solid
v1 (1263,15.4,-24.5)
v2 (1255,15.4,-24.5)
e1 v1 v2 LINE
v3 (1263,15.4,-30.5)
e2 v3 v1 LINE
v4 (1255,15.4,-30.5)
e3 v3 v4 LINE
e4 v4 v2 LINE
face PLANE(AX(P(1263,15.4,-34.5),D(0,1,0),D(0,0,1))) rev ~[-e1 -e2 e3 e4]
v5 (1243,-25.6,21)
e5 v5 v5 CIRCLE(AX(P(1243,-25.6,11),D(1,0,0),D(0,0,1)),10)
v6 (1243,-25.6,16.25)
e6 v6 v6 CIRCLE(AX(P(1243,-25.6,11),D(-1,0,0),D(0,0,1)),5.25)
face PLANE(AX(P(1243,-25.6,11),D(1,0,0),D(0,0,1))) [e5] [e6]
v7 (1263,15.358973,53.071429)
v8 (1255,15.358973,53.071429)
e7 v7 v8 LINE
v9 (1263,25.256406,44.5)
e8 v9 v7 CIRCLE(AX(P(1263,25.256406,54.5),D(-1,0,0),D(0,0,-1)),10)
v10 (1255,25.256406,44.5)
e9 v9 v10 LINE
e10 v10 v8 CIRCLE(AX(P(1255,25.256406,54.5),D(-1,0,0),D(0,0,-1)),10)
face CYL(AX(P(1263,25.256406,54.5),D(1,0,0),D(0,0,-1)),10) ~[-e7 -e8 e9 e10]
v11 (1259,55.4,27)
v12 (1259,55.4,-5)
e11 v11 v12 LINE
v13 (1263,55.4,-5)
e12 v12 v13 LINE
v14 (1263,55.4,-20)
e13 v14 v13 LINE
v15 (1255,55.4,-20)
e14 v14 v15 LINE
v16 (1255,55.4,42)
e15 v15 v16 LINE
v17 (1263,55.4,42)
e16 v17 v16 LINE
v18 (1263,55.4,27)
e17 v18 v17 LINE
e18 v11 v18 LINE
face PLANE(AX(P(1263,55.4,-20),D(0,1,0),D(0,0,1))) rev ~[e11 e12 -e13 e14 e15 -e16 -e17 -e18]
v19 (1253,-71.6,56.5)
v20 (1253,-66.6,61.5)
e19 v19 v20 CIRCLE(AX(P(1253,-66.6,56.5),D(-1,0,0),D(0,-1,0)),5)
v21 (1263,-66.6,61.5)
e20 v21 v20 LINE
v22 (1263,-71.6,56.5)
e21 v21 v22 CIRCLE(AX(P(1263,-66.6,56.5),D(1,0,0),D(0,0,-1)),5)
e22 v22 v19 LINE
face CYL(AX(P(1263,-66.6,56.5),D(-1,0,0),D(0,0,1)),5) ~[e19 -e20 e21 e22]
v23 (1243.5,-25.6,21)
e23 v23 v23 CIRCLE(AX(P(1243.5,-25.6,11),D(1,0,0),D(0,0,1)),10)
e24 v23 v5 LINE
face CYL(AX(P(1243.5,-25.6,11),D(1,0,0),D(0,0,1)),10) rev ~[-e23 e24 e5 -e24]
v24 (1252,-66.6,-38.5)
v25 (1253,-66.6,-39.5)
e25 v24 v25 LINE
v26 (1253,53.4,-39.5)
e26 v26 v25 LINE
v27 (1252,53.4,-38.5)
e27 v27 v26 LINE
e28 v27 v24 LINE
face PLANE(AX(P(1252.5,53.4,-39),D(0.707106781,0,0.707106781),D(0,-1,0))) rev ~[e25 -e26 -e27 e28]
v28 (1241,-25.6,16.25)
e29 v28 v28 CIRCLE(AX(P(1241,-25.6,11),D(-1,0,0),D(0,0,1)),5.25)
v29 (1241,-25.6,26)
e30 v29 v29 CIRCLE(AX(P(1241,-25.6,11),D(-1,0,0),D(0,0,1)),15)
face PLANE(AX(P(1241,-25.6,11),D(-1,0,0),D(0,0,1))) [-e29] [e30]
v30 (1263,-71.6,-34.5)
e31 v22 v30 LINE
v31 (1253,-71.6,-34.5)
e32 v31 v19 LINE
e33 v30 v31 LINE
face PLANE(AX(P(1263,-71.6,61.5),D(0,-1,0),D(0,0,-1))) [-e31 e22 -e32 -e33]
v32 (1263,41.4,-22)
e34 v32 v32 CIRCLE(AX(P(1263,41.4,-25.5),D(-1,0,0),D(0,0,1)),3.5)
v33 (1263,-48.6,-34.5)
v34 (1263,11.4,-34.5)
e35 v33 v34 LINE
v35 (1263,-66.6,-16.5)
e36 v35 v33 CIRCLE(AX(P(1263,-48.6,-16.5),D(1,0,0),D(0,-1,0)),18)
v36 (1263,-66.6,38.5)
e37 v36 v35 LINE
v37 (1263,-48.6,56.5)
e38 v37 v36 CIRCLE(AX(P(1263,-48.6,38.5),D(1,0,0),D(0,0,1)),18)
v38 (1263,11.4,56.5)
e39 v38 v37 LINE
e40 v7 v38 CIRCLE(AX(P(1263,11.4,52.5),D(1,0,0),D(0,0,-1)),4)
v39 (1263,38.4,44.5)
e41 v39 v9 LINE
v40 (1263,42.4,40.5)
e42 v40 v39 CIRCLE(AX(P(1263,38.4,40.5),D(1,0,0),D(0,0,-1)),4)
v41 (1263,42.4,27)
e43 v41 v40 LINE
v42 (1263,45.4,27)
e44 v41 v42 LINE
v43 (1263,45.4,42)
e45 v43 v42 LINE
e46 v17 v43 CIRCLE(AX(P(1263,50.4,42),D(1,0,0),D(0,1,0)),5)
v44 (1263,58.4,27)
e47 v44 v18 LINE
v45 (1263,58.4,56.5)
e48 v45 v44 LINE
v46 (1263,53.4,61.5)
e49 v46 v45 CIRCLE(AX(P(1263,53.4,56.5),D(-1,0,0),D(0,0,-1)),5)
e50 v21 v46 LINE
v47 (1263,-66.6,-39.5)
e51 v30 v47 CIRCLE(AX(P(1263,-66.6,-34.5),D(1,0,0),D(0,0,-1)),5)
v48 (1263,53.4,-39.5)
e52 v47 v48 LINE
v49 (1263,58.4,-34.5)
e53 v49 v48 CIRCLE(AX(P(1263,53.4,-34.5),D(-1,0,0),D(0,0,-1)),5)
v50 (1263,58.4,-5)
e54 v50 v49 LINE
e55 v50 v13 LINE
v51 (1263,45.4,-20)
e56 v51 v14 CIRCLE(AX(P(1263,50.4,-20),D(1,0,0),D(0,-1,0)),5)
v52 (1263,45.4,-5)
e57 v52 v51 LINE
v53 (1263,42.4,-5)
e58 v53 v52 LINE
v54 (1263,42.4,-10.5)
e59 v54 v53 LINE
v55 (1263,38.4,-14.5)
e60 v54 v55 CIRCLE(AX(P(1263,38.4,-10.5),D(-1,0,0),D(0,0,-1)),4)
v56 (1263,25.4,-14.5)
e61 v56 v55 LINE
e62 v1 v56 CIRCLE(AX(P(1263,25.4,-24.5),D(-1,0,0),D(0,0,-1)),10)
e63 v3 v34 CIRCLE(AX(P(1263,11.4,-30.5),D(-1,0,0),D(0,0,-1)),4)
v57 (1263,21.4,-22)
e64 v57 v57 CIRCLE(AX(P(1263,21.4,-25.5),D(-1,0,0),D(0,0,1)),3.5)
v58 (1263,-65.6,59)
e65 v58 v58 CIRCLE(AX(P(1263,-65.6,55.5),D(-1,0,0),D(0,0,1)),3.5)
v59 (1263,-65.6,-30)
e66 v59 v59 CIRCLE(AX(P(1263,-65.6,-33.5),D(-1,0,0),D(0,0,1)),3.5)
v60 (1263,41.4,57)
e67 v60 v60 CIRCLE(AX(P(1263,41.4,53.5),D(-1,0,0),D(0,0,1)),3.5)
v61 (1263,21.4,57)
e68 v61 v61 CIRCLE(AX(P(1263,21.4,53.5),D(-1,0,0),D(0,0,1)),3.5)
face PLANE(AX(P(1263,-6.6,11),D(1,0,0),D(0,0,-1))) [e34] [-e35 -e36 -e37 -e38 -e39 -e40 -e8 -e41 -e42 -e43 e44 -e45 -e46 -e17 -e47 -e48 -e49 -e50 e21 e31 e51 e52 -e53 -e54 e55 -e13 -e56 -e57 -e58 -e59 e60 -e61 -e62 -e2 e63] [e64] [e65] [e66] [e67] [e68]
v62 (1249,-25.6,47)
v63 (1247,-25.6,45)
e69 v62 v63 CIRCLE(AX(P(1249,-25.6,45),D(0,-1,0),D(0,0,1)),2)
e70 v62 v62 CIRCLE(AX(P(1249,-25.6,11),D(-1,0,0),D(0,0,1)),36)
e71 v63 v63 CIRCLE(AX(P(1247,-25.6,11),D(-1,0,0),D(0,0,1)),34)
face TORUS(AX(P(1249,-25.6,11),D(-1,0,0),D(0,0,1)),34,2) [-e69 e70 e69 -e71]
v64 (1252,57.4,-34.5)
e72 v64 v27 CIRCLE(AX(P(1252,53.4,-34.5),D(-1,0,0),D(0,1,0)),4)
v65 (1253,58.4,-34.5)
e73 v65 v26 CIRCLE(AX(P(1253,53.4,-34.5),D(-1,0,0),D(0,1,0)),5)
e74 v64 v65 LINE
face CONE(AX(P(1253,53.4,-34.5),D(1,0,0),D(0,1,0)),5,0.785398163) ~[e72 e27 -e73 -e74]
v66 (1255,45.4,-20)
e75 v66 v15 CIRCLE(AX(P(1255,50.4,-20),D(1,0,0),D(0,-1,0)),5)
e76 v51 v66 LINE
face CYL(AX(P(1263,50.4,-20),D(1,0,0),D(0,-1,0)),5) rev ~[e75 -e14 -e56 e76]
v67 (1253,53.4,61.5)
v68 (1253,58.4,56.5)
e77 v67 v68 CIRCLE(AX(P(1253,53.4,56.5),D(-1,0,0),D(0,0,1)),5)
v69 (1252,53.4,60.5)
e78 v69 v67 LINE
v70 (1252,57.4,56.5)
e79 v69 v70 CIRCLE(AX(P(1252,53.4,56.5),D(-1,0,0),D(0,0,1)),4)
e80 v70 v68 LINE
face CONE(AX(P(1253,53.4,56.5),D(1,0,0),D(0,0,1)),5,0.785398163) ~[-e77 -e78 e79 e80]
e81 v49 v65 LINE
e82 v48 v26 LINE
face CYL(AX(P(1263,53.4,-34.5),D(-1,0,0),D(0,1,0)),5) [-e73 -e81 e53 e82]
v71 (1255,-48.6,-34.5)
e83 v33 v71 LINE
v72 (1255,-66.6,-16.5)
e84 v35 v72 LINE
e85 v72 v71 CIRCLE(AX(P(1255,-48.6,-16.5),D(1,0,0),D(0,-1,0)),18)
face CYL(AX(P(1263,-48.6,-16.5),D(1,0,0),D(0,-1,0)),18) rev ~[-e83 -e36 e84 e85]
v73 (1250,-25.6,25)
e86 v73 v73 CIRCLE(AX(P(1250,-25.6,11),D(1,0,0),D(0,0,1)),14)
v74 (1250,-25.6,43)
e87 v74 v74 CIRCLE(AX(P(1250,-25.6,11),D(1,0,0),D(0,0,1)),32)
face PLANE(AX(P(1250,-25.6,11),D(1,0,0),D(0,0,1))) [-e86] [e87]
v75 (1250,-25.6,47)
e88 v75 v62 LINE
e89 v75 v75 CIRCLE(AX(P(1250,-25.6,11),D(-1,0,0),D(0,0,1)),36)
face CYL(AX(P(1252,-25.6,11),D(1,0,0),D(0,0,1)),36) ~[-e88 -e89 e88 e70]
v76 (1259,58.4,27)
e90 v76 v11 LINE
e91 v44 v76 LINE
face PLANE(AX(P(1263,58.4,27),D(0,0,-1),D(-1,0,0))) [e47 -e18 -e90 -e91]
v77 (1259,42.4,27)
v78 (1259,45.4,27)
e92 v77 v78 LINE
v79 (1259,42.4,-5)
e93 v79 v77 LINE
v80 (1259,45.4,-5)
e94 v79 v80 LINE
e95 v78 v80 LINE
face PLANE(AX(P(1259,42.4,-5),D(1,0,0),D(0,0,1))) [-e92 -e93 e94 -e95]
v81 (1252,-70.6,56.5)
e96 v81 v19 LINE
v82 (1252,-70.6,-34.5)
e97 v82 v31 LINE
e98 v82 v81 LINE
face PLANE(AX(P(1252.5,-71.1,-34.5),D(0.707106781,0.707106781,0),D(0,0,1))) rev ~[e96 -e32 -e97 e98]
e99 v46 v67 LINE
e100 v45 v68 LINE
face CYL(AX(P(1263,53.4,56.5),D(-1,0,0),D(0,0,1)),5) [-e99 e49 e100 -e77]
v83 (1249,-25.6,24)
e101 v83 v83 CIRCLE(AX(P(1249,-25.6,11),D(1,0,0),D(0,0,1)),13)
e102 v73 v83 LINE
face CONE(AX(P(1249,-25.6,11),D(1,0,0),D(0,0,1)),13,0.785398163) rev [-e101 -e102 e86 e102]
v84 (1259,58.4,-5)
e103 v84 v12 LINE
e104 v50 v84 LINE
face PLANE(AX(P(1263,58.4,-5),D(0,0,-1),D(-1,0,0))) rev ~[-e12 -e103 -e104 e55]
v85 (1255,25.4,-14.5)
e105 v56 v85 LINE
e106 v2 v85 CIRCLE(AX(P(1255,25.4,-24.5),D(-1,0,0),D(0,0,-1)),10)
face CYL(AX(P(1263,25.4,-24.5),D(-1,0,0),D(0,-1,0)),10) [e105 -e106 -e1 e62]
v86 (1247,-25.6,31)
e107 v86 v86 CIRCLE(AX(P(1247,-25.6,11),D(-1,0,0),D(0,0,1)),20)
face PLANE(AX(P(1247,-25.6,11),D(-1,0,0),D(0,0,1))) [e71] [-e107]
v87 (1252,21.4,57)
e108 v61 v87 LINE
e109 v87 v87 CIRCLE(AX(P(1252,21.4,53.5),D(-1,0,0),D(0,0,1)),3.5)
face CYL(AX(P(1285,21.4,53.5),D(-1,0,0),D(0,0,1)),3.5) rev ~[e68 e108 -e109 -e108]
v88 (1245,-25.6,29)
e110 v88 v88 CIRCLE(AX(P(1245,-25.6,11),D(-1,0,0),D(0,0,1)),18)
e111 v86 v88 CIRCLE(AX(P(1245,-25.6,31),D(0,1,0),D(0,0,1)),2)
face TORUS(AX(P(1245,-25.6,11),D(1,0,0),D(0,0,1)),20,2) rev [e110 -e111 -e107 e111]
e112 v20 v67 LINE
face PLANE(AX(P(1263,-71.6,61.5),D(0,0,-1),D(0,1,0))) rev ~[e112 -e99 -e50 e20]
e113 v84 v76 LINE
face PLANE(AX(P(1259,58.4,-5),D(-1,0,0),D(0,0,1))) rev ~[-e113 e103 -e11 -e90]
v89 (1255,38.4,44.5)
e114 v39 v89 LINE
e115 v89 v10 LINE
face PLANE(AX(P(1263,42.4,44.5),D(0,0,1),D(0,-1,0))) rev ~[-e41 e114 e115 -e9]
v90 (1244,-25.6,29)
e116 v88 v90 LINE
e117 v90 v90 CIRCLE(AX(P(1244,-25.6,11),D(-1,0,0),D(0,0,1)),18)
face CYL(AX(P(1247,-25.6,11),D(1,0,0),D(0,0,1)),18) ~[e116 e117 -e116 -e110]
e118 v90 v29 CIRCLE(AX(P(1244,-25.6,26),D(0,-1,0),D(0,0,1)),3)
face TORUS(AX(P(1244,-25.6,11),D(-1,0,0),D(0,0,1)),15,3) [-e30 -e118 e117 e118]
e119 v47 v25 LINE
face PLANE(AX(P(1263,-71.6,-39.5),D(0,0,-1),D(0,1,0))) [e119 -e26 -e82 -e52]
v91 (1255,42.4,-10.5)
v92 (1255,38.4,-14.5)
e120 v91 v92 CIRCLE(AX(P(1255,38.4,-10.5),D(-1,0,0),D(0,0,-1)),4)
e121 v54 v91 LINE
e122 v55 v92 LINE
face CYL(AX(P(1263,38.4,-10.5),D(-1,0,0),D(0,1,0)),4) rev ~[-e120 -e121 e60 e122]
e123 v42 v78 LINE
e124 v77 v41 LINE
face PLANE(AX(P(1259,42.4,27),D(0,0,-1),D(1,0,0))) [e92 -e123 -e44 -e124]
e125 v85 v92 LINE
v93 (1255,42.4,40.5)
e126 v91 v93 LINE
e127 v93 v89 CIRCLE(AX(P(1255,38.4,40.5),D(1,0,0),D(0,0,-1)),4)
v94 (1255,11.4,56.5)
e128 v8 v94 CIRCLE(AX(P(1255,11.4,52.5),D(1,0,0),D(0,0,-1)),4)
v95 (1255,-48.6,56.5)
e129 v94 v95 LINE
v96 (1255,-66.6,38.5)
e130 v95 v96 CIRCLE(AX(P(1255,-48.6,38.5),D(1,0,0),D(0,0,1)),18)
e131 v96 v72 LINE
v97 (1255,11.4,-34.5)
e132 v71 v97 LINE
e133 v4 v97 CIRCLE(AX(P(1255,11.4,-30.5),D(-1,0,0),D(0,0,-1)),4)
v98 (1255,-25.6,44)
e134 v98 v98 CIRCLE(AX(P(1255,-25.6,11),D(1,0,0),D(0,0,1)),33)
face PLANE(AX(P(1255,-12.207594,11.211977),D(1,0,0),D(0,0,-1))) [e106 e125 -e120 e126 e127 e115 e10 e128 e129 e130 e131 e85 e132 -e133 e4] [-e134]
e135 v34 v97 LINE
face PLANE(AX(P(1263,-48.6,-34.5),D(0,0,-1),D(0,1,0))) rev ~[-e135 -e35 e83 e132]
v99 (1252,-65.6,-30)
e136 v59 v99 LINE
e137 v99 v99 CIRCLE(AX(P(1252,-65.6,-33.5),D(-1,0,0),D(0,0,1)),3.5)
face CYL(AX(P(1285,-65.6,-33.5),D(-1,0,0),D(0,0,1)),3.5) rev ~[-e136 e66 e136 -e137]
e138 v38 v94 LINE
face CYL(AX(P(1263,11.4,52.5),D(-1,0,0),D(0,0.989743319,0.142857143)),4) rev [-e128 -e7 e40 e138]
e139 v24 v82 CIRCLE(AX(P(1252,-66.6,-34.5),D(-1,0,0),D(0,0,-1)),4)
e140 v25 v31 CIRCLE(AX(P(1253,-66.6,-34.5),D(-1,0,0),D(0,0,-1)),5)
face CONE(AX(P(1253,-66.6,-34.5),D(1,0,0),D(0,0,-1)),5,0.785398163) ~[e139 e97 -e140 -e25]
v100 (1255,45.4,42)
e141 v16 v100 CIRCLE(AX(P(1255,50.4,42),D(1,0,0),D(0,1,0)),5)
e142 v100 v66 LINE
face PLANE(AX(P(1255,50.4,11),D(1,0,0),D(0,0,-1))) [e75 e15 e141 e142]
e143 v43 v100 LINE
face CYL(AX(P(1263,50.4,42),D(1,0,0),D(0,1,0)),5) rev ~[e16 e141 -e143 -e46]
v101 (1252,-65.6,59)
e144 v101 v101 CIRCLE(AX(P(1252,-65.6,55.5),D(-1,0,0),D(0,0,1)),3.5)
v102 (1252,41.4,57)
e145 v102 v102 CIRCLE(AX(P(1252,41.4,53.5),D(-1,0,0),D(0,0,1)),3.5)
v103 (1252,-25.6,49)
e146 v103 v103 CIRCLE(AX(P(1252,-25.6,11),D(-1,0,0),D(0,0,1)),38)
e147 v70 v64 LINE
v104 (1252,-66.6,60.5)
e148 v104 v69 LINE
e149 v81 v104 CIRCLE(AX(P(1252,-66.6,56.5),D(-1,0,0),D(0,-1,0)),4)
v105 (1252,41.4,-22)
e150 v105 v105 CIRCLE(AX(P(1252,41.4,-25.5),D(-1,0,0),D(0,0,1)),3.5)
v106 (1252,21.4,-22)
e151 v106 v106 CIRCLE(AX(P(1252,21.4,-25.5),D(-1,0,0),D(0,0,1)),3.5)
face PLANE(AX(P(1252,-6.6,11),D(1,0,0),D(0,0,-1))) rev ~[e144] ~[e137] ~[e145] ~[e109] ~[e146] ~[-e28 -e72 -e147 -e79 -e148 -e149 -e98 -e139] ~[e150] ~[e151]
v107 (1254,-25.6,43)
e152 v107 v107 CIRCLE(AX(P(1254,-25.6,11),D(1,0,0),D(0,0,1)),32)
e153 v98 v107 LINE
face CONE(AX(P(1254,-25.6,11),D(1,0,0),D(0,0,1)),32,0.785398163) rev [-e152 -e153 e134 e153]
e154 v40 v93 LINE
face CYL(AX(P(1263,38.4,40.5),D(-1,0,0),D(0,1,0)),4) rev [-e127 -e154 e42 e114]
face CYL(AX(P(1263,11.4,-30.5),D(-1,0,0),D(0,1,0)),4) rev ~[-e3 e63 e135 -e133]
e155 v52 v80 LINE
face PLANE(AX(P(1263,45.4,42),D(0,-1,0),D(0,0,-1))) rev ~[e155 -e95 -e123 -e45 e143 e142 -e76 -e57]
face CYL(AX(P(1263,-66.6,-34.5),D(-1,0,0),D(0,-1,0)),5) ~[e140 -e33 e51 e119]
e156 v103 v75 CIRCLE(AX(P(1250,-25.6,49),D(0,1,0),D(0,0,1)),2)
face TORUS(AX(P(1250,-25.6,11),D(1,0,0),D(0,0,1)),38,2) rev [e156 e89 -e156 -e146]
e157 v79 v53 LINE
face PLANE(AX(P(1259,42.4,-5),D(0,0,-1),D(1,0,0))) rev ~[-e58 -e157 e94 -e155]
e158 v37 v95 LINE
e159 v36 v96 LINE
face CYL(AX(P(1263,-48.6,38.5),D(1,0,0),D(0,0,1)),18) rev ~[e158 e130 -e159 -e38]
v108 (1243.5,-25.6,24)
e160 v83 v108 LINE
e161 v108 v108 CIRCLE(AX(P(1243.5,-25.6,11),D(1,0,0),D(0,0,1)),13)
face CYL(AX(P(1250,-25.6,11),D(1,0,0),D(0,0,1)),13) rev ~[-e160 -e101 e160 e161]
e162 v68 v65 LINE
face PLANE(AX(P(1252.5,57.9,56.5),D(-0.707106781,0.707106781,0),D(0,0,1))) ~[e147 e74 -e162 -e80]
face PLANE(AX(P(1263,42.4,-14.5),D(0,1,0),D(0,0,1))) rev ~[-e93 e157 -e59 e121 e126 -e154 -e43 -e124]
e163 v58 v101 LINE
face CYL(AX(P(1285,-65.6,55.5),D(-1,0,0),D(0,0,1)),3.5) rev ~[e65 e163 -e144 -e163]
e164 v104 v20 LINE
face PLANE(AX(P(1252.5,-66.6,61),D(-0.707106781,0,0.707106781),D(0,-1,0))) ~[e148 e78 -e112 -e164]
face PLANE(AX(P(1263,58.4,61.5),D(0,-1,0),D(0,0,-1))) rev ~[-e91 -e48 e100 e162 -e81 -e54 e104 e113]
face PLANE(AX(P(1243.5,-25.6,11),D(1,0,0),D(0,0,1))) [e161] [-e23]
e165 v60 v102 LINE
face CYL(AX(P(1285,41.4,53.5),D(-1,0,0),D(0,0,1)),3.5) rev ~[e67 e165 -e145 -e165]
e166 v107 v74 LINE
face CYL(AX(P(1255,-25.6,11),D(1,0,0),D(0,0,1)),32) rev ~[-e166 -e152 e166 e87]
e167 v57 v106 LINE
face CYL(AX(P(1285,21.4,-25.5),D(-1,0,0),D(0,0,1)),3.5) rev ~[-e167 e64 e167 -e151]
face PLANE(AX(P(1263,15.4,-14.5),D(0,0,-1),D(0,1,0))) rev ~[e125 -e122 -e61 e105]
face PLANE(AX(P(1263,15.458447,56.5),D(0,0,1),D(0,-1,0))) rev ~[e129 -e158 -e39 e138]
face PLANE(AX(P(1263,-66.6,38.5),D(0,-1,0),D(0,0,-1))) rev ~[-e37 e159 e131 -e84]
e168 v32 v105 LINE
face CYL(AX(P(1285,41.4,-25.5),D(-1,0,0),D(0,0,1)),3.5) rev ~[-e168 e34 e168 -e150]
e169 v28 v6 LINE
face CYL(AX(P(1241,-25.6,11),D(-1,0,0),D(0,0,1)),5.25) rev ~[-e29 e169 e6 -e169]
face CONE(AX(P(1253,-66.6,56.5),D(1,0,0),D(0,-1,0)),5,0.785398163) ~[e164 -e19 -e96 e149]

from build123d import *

# Parameters (mm, degrees)
SKETCH_1_W                = 101
SKETCH_1_H                = 130
EXTRUDE_1_DEPTH           = 11
CUT_EXTRUDE_1_DEPTH       = 8
CUT_EXTRUDE_2_DEPTH       = 8
CUT_EXTRUDE_3_REACH       = 1271.625
SKETCH_4_W                = 4
SKETCH_4_H                = 32
CUT_EXTRUDE_4_REACH       = 1273.161
SKETCH_5_W                = 4
SKETCH_5_H                = 32
SKETCH_6_R                = 36
EXTRUDE_2_DEPTH           = 5
SKETCH_7_R                = 18
EXTRUDE_3_DEPTH           = 6
SKETCH_8_R                = 32
CUT_EXTRUDE_5_DEPTH       = 5
SKETCH_9_R                = 13
CUT_EXTRUDE_6_DEPTH       = 6.5
SKETCH_10_R               = 10
CUT_EXTRUDE_7_DEPTH       = 0.5
SKETCH_11_R               = 5.25
CUT_EXTRUDE_8_DEPTH       = 97.916510461
HOLE_WIZARD_7_0_7_1_D     = 7
HOLE_WIZARD_7_0_7_1_DEPTH = 22
FILLET_1_R                = 5
CHAMFER_1_SIZE            = 1
FILLET_2_R                = 2
FILLET_3_R                = 3
FILLET_4_R                = 4
FILLET_5_R                = 10


with BuildPart() as part:
    # 草图1 → 凸台-拉伸1 (new body)
    with BuildSketch(Plane(origin=(1263, 0, 0), x_dir=(0, 0, -1), z_dir=(1, 0, 0))):
        with Locations((-11, -6.6)):
            Rectangle(SKETCH_1_W, SKETCH_1_H)
    extrude(amount=-EXTRUDE_1_DEPTH)

    # 草图2 → 切除-拉伸1 (cut)
    with BuildSketch(Plane(origin=(1263, 0, 0), x_dir=(0, 0, -1), z_dir=(1, 0, 0))):
        with BuildLine():
            Line((14.5, 42.4), (-44.5, 42.4))
            Line((-44.5, 42.4), (-44.5, 25.256406461))
            ThreePointArc((-44.5, 25.256406461), (-48.17544468, 17.510439768), (-56.5, 15.458447489))
            Line((-56.5, 15.458447489), (-56.5, -48.6))
            ThreePointArc((-56.5, -48.6), (-51.227922061, -61.327922061), (-38.5, -66.6))
            Line((-38.5, -66.6), (16.5, -66.6))
            ThreePointArc((16.5, -66.6), (29.227922061, -61.327922061), (34.5, -48.6))
            Line((34.5, -48.6), (34.5, 15.4))
            Line((34.5, 15.4), (14.5, 15.4))
            Line((14.5, 15.4), (14.5, 42.4))
        make_face()
    extrude(amount=-CUT_EXTRUDE_1_DEPTH, mode=Mode.SUBTRACT)

    # 草图3 → 切除-拉伸2 (cut)
    with BuildSketch(Plane(origin=(1263, 0, 0), x_dir=(0, 0, -1), z_dir=(1, 0, 0))):
        with BuildLine():
            Line((20, 55.4), (-42, 55.4))
            ThreePointArc((-42, 55.4), (-47, 50.4), (-42, 45.4))
            Line((-42, 45.4), (20, 45.4))
            ThreePointArc((20, 45.4), (25, 50.4), (20, 55.4))
        make_face()
    extrude(amount=-CUT_EXTRUDE_2_DEPTH, mode=Mode.SUBTRACT)

    # 草图4 → 切除-拉伸3 (cut, up to next)
    with BuildSketch(Plane.XZ.offset(-42.4), mode=Mode.PRIVATE) as cut_extrude_3_sk1:
        with Locations((1261, 11)):
            Rectangle(SKETCH_4_W, SKETCH_4_H)
    cut_extrude_3_tool1 = extrude(cut_extrude_3_sk1.sketch, amount=-CUT_EXTRUDE_3_REACH, mode=Mode.PRIVATE) & part.part
    add(cut_extrude_3_tool1.solids().sort_by_distance((1261, 42.4, 11))[0], mode=Mode.SUBTRACT)

    # 草图5 → 切除-拉伸4 (cut, up to next)
    with BuildSketch(Plane(origin=(0, 58.4, 0), x_dir=(-1, 0, 0), z_dir=(0, 1, 0)), mode=Mode.PRIVATE) as cut_extrude_4_sk1:
        with Locations((-1261, 11)):
            Rectangle(SKETCH_5_W, SKETCH_5_H)
    cut_extrude_4_tool1 = extrude(cut_extrude_4_sk1.sketch, amount=-CUT_EXTRUDE_4_REACH, mode=Mode.PRIVATE) & part.part
    add(cut_extrude_4_tool1.solids().sort_by_distance((1261, 58.4, 11))[0], mode=Mode.SUBTRACT)

    # 草图6 → 凸台-拉伸2 (add)
    with BuildSketch(Plane.ZY.offset(-1252)):
        with Locations((11, -25.6)):
            Circle(SKETCH_6_R)
    extrude(amount=EXTRUDE_2_DEPTH)

    # 草图7 → 凸台-拉伸3 (add)
    with BuildSketch(Plane.ZY.offset(-1247)):
        with Locations((11, -25.6)):
            Circle(SKETCH_7_R)
    extrude(amount=EXTRUDE_3_DEPTH)

    # 草图8 → 切除-拉伸5 (cut)
    with BuildSketch(Plane(origin=(1255, 0, 0), x_dir=(0, 0, -1), z_dir=(1, 0, 0))):
        with Locations(Location((-11, -25.6, 0), (0, 0, 180))):
            Circle(SKETCH_8_R)
    extrude(amount=-CUT_EXTRUDE_5_DEPTH, mode=Mode.SUBTRACT)

    # 草图9 → 切除-拉伸6 (cut)
    with BuildSketch(Plane(origin=(1250, 0, 0), x_dir=(0, 0, -1), z_dir=(1, 0, 0))):
        with Locations(Location((-11, -25.6, 0), (0, 0, 180))):
            Circle(SKETCH_9_R)
    extrude(amount=-CUT_EXTRUDE_6_DEPTH, mode=Mode.SUBTRACT)

    # 草图10 → 切除-拉伸7 (cut)
    with BuildSketch(Plane(origin=(1243.5, 0, 0), x_dir=(0, 0, -1), z_dir=(1, 0, 0))):
        with Locations(Location((-11, -25.6, 0), (0, 0, 180))):
            Circle(SKETCH_10_R)
    extrude(amount=-CUT_EXTRUDE_7_DEPTH, mode=Mode.SUBTRACT)

    # 草图11 → 切除-拉伸8 (cut, through all)
    with BuildSketch(Plane.ZY.offset(-1241)):
        with Locations((11, -25.6)):
            Circle(SKETCH_11_R)
    extrude(amount=-CUT_EXTRUDE_8_DEPTH, mode=Mode.SUBTRACT)

    # Ø7.0 (7) 直径孔1
    with Locations(Plane(origin=(1263, 0, 0), x_dir=(0, 0, -1), z_dir=(1, 0, 0))):
        with Locations((-55.5, -65.6), (33.5, -65.6), (25.5, 21.4), (25.5, 41.4), (-53.5, 41.4), (-53.5, 21.4)):
            Hole(HOLE_WIZARD_7_0_7_1_D / 2, depth=HOLE_WIZARD_7_0_7_1_DEPTH)

    # 圆角1
    fillet_1_edges = [part.edges().sort_by_distance(p)[0] for p in [
        (1257.5, -71.6, -39.5),
        (1257.5, -71.6, 61.5),
        (1257.5, 58.4, 61.5),
        (1257.5, 58.4, -39.5),
    ]]
    fillet(fillet_1_edges, radius=FILLET_1_R)

    # 倒角1
    chamfer_1_edges = [part.edges().sort_by_distance(p)[0] for p in [
        (1252, 58.4, 11),
        (1252, -6.6, 61.5),
        (1252, -6.6, -39.5),
        (1252, -71.6, 11),
        (1252, -70.135533906, 60.035533906),
        (1252, -70.135533906, -38.035533906),
        (1252, 56.935533906, -38.035533906),
        (1252, 56.935533906, 60.035533906),
        (1255, -25.6, -21),
        (1250, -25.6, -2),
    ]]
    chamfer(chamfer_1_edges, length=CHAMFER_1_SIZE)

    # 圆角2
    fillet_2_edges = [part.edges().sort_by_distance(p)[0] for p in [
        (1252, -25.6, -25),
        (1247, -25.6, -25),
        (1247, -25.6, -7),
    ]]
    fillet(fillet_2_edges, radius=FILLET_2_R)

    # 圆角3
    fillet_3_edges = [part.edges().sort_by_distance(p)[0] for p in [
        (1241, -25.6, -7),
    ]]
    fillet(fillet_3_edges, radius=FILLET_3_R)

    # 圆角4
    fillet_4_edges = [part.edges().sort_by_distance(p)[0] for p in [
        (1259, 42.4, -14.5),
        (1259, 15.4, -34.5),
        (1259, 15.458447489, 56.5),
        (1259, 42.4, 44.5),
    ]]
    fillet(fillet_4_edges, radius=FILLET_4_R)

    # 圆角5
    fillet_5_edges = [part.edges().sort_by_distance(p)[0] for p in [
        (1259, 15.4, -14.5),
    ]]
    fillet(fillet_5_edges, radius=FILLET_5_R)


solid = part.part
